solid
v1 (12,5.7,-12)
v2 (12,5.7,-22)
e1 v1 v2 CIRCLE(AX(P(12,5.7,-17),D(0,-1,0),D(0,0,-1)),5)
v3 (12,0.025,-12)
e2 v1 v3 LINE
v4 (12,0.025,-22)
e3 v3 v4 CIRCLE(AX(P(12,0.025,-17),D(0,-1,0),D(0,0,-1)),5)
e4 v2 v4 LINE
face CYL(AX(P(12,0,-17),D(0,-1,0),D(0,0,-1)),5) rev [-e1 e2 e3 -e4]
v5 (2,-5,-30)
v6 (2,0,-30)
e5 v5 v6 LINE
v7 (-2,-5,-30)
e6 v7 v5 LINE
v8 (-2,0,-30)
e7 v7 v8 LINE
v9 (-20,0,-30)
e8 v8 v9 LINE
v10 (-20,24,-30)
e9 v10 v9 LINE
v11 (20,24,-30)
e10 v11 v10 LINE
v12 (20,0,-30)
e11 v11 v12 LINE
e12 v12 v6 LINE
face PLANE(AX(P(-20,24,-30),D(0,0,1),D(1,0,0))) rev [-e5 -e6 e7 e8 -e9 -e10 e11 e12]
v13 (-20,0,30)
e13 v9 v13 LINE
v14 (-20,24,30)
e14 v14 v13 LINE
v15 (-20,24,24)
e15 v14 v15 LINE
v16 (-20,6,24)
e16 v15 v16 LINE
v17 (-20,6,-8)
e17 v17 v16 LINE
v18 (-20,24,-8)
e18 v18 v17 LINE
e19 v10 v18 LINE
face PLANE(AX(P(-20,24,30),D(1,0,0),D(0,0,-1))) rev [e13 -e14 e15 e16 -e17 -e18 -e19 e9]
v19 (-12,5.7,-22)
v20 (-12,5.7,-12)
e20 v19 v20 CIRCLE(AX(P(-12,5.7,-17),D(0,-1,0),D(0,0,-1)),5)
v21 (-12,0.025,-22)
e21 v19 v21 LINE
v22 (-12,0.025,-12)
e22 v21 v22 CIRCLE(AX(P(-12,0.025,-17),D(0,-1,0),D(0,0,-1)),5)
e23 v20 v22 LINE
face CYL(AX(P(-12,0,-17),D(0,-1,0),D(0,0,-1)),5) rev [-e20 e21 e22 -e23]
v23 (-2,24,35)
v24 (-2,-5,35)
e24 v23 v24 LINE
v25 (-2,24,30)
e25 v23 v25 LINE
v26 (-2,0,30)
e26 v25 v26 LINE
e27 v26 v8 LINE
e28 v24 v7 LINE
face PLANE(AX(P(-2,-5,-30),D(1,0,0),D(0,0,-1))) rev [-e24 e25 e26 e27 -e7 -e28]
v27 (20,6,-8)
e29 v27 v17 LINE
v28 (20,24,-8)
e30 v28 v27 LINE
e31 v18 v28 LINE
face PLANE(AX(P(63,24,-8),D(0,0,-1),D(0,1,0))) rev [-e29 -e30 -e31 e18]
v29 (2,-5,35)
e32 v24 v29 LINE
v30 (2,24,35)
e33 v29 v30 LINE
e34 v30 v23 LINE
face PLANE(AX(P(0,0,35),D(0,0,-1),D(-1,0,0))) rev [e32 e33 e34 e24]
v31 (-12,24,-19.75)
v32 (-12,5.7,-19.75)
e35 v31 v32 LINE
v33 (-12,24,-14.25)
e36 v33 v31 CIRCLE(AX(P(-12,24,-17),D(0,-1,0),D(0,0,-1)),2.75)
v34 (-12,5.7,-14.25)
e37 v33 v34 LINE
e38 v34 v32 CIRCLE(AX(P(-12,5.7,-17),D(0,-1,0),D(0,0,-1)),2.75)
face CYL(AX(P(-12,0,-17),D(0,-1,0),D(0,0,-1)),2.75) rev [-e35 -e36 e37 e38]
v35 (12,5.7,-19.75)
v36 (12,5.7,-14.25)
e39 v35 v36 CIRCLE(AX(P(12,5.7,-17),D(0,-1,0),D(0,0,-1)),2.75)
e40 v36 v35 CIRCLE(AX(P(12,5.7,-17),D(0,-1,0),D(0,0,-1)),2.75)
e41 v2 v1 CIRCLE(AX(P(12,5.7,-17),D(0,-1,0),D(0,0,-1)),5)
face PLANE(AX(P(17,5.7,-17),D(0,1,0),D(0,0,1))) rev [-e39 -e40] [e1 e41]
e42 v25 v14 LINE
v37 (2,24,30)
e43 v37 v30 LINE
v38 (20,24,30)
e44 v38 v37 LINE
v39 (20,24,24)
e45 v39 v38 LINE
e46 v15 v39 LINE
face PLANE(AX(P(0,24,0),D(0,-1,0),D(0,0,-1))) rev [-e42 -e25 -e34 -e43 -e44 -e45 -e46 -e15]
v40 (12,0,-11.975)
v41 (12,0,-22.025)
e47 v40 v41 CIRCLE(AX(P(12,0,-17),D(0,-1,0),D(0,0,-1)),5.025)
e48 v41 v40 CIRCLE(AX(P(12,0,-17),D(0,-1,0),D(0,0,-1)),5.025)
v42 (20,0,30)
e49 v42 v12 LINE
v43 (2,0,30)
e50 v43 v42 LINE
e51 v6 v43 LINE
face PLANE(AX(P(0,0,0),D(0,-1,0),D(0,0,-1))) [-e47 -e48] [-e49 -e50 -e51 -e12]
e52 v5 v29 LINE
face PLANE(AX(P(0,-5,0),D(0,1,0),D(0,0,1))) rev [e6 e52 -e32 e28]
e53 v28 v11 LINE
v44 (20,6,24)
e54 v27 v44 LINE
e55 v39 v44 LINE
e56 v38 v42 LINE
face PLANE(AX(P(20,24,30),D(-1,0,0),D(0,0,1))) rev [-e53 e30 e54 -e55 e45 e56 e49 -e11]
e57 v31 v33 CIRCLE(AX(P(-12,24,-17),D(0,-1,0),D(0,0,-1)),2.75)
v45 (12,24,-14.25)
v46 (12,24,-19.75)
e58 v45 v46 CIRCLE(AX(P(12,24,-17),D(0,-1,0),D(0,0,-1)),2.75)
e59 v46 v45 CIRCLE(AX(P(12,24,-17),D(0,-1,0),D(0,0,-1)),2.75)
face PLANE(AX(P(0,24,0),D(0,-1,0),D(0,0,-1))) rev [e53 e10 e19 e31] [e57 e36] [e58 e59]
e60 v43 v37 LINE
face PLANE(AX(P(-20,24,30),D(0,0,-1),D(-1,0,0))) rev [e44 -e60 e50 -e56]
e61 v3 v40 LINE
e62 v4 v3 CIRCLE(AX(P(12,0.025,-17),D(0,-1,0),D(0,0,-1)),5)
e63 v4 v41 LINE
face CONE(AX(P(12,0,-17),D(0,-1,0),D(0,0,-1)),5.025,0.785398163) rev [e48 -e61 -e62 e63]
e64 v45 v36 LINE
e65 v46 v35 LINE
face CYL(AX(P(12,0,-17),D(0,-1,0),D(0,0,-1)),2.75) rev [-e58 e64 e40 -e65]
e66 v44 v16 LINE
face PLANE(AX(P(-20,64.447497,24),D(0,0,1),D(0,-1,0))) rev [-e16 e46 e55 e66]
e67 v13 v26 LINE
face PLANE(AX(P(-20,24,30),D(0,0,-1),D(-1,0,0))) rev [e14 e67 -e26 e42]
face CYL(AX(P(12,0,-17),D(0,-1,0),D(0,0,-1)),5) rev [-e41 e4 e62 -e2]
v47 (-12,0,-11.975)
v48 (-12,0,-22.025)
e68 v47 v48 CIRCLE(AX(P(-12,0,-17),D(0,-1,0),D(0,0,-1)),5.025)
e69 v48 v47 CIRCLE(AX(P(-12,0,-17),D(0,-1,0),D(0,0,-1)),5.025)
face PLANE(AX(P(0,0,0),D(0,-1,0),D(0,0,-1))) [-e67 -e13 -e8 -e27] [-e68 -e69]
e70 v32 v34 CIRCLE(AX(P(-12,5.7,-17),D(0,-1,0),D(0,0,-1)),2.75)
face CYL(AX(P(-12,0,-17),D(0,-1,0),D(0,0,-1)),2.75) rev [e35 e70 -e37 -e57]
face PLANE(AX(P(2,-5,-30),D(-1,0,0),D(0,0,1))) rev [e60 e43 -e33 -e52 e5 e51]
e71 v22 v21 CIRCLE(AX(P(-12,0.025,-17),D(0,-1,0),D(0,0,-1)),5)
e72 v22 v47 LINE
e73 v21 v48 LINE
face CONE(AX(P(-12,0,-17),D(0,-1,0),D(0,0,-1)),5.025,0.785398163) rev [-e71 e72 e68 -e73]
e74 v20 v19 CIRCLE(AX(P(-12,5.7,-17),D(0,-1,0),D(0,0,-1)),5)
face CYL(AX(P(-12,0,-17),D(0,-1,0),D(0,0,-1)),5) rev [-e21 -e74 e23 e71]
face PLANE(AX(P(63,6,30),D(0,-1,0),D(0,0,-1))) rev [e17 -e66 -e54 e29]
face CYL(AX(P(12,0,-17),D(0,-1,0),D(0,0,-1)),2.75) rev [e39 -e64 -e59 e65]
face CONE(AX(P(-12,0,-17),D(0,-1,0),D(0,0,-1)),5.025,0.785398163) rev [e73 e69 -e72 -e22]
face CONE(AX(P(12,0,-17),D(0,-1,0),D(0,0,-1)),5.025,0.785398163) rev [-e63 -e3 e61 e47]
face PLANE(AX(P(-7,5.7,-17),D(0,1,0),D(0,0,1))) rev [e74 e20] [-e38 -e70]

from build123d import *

# Parameters (mm, degrees)
SKETCH1_W                                    = 40
SKETCH1_H                                    = 60
BOSS_EXTRUDE1_DEPTH                          = 24
SKETCH4_W                                    = 38
SKETCH4_H                                    = 18
CUT_EXTRUDE2_DEPTH                           = 83
SKETCH5_W                                    = 4
SKETCH5_H                                    = 60
BOSS_EXTRUDE2_DEPTH                          = 5
SKETCH6_W                                    = 4
SKETCH6_H                                    = 11
BOSS_EXTRUDE3_DEPTH                          = 5
SKETCH7_W                                    = 40
SKETCH7_H                                    = 6
BOSS_EXTRUDE4_DEPTH                          = 18
CBORE_FOR_M5_HEXAGON_SOCKET_HEAD_CAP_2_COUNT = 2
CBORE_FOR_M5_HEXAGON_SOCKET_HEAD_CAP_2_PITCH = 24
SKETCH11_W                                   = 4
SKETCH11_H                                   = 5
BOSS_EXTRUDE5_DEPTH                          = 18


with BuildPart() as part:
    # Sketch1 → Boss-Extrude1 (new body)
    with BuildSketch(Plane(origin=(0, 0, 0), x_dir=(1, 0, 0), z_dir=(0, 1, 0))):
        Rectangle(SKETCH1_W, SKETCH1_H)
    extrude(amount=BOSS_EXTRUDE1_DEPTH)

    # Sketch4 → Cut-Extrude2 (cut)
    with BuildSketch(Plane.ZY.offset(20)):
        with Locations((11, 15)):
            Rectangle(SKETCH4_W, SKETCH4_H)
    extrude(amount=-CUT_EXTRUDE2_DEPTH, mode=Mode.SUBTRACT)

    # Sketch5 → Boss-Extrude2 (add)
    with BuildSketch(Plane.XZ):
        Rectangle(SKETCH5_W, SKETCH5_H)
    extrude(amount=BOSS_EXTRUDE2_DEPTH)

    # Sketch6 → Boss-Extrude3 (add)
    with BuildSketch(Plane.XY.offset(30)):
        with Locations((0, 0.5)):
            Rectangle(SKETCH6_W, SKETCH6_H)
    extrude(amount=BOSS_EXTRUDE3_DEPTH)

    # Sketch7 → Boss-Extrude4 (add)
    with BuildSketch(Plane(origin=(0, 6, 0), x_dir=(1, 0, 0), z_dir=(0, 1, 0))):
        with Locations((0, -27)):
            Rectangle(SKETCH7_W, SKETCH7_H)
    extrude(amount=BOSS_EXTRUDE4_DEPTH)

    # Sketch10 → CBORE for M5 Hexagon socket head cap screws1 (revolve, cut)
    with BuildSketch(Plane(origin=(12, 0, -17), x_dir=(0, 0, -1), z_dir=(1, 0, 0))):
        Polygon((0, 0), (0, 24), (2.75, 24), (2.75, 5.7), (5, 5.7), (5, 0.025), (5.025, 0), align=None)
    cbore_for_m5_hexagon_socket_head_cap_scr = revolve(axis=Axis((12, -6.35, -17), (0, 1, 0)), mode=Mode.SUBTRACT)

    # CBORE for M5 Hexagon socket head cap 2: CBORE for M5 Hexagon socket head cap screws1 ×2
    with Locations(*[(-i * CBORE_FOR_M5_HEXAGON_SOCKET_HEAD_CAP_2_PITCH, 0, 0) for i in range(1, CBORE_FOR_M5_HEXAGON_SOCKET_HEAD_CAP_2_COUNT)]):
        add(cbore_for_m5_hexagon_socket_head_cap_scr, mode=Mode.SUBTRACT)

    # Sketch11 → Boss-Extrude5 (add)
    with BuildSketch(Plane(origin=(0, 6, 0), x_dir=(1, 0, 0), z_dir=(0, 1, 0))):
        with Locations((0, -32.5)):
            Rectangle(SKETCH11_W, SKETCH11_H)
    extrude(amount=BOSS_EXTRUDE5_DEPTH)


solid = part.part
